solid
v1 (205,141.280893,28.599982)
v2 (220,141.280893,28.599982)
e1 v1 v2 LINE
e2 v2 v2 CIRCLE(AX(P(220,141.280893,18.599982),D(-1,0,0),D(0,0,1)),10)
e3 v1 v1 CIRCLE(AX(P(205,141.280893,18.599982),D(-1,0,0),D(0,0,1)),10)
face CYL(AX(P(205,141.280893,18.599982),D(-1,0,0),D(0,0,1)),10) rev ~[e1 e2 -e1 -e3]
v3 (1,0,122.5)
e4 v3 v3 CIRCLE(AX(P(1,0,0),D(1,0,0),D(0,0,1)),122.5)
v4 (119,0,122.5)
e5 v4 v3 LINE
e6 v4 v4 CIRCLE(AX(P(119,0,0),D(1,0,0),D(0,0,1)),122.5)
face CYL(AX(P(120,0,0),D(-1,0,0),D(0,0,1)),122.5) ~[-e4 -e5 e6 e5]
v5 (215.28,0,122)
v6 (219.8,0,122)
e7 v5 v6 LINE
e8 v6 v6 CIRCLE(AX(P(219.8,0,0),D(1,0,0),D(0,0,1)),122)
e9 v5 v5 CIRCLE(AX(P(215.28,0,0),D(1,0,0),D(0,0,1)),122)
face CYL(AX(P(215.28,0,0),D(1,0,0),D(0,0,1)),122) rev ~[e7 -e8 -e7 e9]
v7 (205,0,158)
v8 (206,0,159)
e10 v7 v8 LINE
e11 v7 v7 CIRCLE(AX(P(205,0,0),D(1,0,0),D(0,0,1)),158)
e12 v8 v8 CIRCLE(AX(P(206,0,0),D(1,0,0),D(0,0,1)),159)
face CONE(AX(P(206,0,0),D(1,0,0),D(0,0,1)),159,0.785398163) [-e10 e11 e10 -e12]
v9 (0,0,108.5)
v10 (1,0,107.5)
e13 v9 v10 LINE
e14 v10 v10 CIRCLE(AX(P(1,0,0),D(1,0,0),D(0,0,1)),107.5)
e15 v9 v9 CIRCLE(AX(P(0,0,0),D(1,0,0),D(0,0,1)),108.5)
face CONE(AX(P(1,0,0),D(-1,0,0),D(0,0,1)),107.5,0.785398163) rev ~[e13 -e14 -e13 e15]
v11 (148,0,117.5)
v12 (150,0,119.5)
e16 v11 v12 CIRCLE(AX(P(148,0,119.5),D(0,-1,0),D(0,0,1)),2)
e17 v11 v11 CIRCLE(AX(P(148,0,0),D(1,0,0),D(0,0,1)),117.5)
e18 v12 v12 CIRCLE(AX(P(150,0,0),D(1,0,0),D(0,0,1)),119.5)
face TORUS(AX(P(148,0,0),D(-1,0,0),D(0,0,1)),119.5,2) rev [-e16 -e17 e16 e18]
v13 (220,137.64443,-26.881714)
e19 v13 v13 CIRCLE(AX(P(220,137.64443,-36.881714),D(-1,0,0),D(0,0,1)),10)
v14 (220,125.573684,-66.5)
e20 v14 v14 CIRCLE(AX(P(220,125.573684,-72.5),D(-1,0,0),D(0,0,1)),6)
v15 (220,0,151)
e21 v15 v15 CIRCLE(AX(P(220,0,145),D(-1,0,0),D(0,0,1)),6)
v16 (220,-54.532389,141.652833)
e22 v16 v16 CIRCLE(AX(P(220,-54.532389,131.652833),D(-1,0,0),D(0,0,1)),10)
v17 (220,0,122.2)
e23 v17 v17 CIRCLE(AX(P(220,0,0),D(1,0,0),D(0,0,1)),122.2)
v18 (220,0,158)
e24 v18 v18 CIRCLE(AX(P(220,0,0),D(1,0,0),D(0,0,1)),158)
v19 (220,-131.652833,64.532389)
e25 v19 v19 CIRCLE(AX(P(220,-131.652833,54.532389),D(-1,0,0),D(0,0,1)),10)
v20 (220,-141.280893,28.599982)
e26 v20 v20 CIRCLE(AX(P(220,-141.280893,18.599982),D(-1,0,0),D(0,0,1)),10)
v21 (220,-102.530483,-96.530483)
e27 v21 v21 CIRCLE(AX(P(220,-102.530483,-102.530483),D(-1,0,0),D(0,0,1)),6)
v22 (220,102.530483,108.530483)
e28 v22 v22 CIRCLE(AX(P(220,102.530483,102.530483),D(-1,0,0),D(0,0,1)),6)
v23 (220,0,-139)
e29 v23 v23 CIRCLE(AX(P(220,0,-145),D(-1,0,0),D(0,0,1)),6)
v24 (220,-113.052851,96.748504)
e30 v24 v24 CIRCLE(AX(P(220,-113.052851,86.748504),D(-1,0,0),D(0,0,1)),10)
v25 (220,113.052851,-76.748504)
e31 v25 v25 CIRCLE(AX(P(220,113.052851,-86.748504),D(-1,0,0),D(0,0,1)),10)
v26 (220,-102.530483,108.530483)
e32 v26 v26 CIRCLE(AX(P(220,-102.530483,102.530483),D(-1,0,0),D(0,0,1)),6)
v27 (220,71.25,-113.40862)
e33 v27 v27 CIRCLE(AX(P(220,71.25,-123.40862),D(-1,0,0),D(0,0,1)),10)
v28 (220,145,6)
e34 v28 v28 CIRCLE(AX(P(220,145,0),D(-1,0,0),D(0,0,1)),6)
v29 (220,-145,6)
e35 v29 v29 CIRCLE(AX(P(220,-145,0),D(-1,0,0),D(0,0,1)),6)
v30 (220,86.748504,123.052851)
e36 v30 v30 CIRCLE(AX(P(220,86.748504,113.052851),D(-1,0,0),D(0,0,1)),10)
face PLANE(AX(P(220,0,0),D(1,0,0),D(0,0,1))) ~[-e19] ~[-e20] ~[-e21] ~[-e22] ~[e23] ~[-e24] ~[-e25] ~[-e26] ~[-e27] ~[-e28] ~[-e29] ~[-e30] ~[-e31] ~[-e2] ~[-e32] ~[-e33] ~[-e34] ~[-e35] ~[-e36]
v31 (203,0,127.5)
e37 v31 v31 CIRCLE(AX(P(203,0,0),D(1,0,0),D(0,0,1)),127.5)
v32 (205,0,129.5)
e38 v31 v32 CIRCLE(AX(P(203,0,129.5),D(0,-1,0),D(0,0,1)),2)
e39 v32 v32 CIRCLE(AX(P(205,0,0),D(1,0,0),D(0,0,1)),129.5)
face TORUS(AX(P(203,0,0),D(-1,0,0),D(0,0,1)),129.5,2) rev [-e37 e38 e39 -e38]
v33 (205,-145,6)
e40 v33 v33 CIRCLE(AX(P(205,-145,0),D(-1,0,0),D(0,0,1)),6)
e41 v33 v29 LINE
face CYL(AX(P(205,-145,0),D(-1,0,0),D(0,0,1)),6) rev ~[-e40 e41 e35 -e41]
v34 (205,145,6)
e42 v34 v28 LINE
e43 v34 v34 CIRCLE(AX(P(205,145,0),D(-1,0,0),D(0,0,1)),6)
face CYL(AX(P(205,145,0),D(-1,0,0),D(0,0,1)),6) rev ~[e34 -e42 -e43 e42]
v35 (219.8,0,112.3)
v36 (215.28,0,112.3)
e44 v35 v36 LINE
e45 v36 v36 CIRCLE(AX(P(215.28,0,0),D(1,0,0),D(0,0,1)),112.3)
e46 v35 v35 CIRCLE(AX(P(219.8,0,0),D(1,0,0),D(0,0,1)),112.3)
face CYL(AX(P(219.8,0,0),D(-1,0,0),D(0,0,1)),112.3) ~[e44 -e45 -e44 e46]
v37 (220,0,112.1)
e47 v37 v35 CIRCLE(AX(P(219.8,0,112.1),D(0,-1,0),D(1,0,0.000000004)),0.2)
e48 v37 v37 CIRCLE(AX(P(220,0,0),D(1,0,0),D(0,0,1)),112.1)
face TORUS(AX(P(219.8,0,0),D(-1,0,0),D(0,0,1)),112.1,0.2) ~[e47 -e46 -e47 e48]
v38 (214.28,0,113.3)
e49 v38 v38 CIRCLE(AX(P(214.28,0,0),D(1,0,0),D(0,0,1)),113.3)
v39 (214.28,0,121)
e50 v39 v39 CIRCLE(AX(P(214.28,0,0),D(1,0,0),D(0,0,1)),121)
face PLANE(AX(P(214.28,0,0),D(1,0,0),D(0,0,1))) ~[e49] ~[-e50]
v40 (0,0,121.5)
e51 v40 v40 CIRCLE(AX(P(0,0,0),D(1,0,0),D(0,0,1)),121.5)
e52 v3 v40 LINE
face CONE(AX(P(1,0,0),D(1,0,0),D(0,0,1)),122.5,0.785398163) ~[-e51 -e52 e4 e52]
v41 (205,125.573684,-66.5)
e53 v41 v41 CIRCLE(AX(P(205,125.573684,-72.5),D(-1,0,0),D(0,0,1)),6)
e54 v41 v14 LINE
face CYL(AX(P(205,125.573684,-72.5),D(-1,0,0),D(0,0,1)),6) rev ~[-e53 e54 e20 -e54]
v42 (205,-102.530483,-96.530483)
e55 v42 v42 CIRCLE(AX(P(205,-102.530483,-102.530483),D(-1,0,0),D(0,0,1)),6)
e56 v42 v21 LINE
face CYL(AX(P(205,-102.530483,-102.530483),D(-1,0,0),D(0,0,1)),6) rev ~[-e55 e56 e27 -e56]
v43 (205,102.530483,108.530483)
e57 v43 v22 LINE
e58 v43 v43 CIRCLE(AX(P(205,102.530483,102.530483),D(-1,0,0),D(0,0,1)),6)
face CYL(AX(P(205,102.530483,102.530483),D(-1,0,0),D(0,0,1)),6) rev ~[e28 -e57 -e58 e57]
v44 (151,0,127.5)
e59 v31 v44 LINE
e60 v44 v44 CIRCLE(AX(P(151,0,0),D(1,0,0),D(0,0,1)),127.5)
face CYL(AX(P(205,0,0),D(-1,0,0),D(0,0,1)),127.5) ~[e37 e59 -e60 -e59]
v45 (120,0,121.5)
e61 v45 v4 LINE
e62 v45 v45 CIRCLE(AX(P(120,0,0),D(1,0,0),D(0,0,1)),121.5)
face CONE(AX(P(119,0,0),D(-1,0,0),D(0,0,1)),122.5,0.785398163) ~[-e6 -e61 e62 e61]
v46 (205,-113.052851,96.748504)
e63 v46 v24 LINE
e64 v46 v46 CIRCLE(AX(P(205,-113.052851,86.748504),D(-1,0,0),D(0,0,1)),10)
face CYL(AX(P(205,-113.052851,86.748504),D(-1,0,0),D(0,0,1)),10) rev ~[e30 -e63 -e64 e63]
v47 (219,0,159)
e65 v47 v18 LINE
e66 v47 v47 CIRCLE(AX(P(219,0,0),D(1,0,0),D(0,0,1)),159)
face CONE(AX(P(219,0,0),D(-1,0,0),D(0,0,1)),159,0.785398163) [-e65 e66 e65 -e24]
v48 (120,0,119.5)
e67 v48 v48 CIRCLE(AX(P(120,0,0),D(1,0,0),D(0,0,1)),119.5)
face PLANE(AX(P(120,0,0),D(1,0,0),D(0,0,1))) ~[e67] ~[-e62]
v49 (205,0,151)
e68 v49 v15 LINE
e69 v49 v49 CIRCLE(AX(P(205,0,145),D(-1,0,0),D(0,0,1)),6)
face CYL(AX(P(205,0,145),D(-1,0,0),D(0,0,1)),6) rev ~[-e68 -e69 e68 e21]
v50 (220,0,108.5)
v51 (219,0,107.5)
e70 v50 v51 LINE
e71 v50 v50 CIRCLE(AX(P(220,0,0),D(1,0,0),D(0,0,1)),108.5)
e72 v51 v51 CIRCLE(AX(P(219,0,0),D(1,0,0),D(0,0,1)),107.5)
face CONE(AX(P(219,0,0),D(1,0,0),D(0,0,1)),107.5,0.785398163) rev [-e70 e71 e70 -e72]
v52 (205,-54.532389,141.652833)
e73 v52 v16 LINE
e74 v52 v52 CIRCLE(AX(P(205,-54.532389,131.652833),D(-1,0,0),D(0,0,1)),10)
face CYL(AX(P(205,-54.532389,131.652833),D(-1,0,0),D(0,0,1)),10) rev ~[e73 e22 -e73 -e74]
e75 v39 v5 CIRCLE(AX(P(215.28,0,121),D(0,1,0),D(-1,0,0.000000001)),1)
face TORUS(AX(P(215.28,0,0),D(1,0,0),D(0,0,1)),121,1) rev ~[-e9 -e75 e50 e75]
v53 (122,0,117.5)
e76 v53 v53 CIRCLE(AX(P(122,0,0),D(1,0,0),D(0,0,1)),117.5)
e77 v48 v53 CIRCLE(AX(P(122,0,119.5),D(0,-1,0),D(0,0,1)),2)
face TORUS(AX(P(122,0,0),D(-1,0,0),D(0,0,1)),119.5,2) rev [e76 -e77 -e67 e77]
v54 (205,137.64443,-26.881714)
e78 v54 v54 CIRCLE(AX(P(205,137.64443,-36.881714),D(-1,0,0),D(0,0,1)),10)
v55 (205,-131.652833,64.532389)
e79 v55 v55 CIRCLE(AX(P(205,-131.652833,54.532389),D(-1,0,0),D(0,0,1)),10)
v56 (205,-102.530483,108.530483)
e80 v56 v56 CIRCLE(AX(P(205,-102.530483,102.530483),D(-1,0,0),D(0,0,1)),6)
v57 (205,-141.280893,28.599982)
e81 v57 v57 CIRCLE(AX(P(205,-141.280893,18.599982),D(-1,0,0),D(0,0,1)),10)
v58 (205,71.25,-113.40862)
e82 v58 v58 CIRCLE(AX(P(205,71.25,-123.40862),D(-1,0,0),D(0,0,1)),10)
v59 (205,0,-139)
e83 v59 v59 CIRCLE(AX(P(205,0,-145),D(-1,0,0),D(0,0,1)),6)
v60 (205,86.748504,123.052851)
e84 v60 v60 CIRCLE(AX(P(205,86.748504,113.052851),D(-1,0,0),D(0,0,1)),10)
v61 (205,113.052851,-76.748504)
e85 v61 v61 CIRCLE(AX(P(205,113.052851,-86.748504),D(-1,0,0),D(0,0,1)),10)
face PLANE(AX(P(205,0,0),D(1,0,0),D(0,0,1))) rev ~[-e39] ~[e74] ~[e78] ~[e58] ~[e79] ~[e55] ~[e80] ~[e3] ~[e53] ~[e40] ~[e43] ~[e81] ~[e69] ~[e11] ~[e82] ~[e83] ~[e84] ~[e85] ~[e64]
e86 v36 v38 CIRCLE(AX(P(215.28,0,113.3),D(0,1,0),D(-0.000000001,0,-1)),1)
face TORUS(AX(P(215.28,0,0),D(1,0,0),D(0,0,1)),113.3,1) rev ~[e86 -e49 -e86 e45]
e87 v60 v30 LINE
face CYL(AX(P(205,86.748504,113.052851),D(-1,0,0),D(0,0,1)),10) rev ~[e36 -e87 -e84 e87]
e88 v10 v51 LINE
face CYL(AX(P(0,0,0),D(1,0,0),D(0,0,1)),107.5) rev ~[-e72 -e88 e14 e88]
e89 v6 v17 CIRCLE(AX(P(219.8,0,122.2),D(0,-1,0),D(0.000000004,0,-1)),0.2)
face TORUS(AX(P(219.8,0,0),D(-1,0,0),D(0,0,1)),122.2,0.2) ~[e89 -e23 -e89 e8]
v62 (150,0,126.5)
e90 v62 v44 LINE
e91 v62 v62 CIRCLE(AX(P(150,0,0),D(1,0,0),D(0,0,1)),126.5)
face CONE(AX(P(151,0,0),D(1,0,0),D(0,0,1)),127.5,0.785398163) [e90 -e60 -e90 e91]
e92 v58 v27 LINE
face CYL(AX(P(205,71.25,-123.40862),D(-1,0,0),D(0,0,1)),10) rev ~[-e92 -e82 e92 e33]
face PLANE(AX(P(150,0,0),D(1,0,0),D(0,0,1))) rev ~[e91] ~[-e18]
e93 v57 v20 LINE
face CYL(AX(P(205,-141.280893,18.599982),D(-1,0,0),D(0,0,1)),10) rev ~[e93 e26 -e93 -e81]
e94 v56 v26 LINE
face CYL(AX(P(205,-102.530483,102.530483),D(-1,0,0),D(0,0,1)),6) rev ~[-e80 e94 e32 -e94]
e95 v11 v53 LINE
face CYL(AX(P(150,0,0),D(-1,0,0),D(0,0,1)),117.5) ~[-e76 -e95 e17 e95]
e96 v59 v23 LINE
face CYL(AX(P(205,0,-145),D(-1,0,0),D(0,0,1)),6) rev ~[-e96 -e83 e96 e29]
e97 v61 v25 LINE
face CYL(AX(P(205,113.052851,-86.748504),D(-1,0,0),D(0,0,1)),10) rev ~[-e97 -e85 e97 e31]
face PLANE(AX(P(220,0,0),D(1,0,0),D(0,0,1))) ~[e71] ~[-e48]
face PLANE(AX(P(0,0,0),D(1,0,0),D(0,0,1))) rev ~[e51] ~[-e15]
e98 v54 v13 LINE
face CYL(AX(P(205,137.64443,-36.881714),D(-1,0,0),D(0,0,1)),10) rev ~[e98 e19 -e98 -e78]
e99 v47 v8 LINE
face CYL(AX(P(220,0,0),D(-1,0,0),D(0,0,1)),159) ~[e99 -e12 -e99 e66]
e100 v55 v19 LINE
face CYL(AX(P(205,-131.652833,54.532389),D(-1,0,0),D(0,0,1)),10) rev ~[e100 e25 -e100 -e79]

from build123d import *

# Parameters (mm, degrees)
SKETCH2_R          = 6
CUT_EXTRUDE1_DEPTH = 305.281120019
FILLET1_R          = 2
CHAMFER1_SIZE      = 1
FILLET2_R          = 2
CHAMFER2_SIZE      = 1
SKETCH4_R          = 10
CUT_EXTRUDE2_DEPTH = 305.281120019


with BuildPart() as part:
    # Sketch1 → Revolve1 (revolve)
    with BuildSketch(Plane.XY, mode=Mode.PRIVATE) as revolve1_sk:
        with BuildLine():
            Line((0, 107.5), (220, 107.5))
            Line((220, 107.5), (220, 112.1))
            ThreePointArc((220, 112.1), (219.941421356, 112.241421356), (219.8, 112.3))
            Line((219.8, 112.3), (215.28, 112.3))
            ThreePointArc((215.28, 112.3), (214.572893219, 112.592893219), (214.28, 113.3))
            Line((214.28, 113.3), (214.28, 121))
            ThreePointArc((214.28, 121), (214.572893219, 121.707106781), (215.28, 122))
            Line((215.28, 122), (219.8, 122))
            ThreePointArc((219.8, 122), (219.941421356, 122.058578644), (220, 122.2))
            Line((220, 122.2), (220, 159))
            Line((220, 159), (205, 159))
            Line((205, 159), (205, 127.5))
            Line((205, 127.5), (150, 127.5))
            Line((150, 127.5), (150, 117.5))
            Line((150, 117.5), (120, 117.5))
            Line((120, 117.5), (120, 122.5))
            Line((120, 122.5), (0, 122.5))
            Line((0, 122.5), (0, 107.5))
        make_face()
    revolve(revolve1_sk.sketch.rotate(Axis((0, 0, 0), (1, 0, 0)), 90), axis=Axis((0, 0, 0), (1, 0, 0)))

    # Sketch2 → Cut-Extrude1 (cut, through all)
    with BuildSketch(Plane.ZY.offset(-205)):
        with Locations((-72.5, 125.573683549)):
            Circle(SKETCH2_R)
        with Locations((0, 145)):
            Circle(SKETCH2_R)
        with Locations((102.530483272, 102.530483272)):
            Circle(SKETCH2_R)
        with Locations((145, 0)):
            Circle(SKETCH2_R)
        with Locations((102.530483272, -102.530483272)):
            Circle(SKETCH2_R)
        with Locations((0, -145)):
            Circle(SKETCH2_R)
        with Locations((-102.530483272, -102.530483272)):
            Circle(SKETCH2_R)
        with Locations((-145, 0)):
            Circle(SKETCH2_R)
    extrude(amount=-CUT_EXTRUDE1_DEPTH, mode=Mode.SUBTRACT)

    # Fillet1
    fillet1_edges = [part.edges().sort_by_distance(p)[0] for p in [
        (120, 0, -117.5),
        (150, 0, -117.5),
    ]]
    fillet(fillet1_edges, radius=FILLET1_R)

    # Chamfer1
    chamfer1_edges = [part.edges().sort_by_distance(p)[0] for p in [
        (0, 0, -122.5),
        (120, 0, -122.5),
        (150, 0, -127.5),
        (205, 0, -159),
        (220, 0, -159),
        (0, 0, -107.5),
    ]]
    chamfer(chamfer1_edges, length=CHAMFER1_SIZE)

    # Fillet2
    fillet2_edges = [part.edges().sort_by_distance(p)[0] for p in [
        (205, 0, -127.5),
    ]]
    fillet(fillet2_edges, radius=FILLET2_R)

    # Chamfer2
    chamfer2_edges = [part.edges().sort_by_distance(p)[0] for p in [
        (220, 0, -107.5),
    ]]
    chamfer(chamfer2_edges, length=CHAMFER2_SIZE)

    # Sketch4 → Cut-Extrude2 (cut, through all)
    with BuildSketch(Plane.ZY.offset(-205)):
        with Locations((-123.408620039, 71.25)):
            Circle(SKETCH4_R)
        with Locations((-86.748503634, 113.052850992)):
            Circle(SKETCH4_R)
        with Locations((-36.881713927, 137.644430246)):
            Circle(SKETCH4_R)
        with Locations((18.599982391, 141.280892746)):
            Circle(SKETCH4_R)
        with Locations((113.052850992, 86.748503634)):
            Circle(SKETCH4_R)
        with Locations((131.652833383, -54.532389112)):
            Circle(SKETCH4_R)
        with Locations((86.748503634, -113.052850992)):
            Circle(SKETCH4_R)
        with Locations((54.532389112, -131.652833383)):
            Circle(SKETCH4_R)
        with Locations((18.599982391, -141.280892746)):
            Circle(SKETCH4_R)
    extrude(amount=-CUT_EXTRUDE2_DEPTH, mode=Mode.SUBTRACT)


solid = part.part
